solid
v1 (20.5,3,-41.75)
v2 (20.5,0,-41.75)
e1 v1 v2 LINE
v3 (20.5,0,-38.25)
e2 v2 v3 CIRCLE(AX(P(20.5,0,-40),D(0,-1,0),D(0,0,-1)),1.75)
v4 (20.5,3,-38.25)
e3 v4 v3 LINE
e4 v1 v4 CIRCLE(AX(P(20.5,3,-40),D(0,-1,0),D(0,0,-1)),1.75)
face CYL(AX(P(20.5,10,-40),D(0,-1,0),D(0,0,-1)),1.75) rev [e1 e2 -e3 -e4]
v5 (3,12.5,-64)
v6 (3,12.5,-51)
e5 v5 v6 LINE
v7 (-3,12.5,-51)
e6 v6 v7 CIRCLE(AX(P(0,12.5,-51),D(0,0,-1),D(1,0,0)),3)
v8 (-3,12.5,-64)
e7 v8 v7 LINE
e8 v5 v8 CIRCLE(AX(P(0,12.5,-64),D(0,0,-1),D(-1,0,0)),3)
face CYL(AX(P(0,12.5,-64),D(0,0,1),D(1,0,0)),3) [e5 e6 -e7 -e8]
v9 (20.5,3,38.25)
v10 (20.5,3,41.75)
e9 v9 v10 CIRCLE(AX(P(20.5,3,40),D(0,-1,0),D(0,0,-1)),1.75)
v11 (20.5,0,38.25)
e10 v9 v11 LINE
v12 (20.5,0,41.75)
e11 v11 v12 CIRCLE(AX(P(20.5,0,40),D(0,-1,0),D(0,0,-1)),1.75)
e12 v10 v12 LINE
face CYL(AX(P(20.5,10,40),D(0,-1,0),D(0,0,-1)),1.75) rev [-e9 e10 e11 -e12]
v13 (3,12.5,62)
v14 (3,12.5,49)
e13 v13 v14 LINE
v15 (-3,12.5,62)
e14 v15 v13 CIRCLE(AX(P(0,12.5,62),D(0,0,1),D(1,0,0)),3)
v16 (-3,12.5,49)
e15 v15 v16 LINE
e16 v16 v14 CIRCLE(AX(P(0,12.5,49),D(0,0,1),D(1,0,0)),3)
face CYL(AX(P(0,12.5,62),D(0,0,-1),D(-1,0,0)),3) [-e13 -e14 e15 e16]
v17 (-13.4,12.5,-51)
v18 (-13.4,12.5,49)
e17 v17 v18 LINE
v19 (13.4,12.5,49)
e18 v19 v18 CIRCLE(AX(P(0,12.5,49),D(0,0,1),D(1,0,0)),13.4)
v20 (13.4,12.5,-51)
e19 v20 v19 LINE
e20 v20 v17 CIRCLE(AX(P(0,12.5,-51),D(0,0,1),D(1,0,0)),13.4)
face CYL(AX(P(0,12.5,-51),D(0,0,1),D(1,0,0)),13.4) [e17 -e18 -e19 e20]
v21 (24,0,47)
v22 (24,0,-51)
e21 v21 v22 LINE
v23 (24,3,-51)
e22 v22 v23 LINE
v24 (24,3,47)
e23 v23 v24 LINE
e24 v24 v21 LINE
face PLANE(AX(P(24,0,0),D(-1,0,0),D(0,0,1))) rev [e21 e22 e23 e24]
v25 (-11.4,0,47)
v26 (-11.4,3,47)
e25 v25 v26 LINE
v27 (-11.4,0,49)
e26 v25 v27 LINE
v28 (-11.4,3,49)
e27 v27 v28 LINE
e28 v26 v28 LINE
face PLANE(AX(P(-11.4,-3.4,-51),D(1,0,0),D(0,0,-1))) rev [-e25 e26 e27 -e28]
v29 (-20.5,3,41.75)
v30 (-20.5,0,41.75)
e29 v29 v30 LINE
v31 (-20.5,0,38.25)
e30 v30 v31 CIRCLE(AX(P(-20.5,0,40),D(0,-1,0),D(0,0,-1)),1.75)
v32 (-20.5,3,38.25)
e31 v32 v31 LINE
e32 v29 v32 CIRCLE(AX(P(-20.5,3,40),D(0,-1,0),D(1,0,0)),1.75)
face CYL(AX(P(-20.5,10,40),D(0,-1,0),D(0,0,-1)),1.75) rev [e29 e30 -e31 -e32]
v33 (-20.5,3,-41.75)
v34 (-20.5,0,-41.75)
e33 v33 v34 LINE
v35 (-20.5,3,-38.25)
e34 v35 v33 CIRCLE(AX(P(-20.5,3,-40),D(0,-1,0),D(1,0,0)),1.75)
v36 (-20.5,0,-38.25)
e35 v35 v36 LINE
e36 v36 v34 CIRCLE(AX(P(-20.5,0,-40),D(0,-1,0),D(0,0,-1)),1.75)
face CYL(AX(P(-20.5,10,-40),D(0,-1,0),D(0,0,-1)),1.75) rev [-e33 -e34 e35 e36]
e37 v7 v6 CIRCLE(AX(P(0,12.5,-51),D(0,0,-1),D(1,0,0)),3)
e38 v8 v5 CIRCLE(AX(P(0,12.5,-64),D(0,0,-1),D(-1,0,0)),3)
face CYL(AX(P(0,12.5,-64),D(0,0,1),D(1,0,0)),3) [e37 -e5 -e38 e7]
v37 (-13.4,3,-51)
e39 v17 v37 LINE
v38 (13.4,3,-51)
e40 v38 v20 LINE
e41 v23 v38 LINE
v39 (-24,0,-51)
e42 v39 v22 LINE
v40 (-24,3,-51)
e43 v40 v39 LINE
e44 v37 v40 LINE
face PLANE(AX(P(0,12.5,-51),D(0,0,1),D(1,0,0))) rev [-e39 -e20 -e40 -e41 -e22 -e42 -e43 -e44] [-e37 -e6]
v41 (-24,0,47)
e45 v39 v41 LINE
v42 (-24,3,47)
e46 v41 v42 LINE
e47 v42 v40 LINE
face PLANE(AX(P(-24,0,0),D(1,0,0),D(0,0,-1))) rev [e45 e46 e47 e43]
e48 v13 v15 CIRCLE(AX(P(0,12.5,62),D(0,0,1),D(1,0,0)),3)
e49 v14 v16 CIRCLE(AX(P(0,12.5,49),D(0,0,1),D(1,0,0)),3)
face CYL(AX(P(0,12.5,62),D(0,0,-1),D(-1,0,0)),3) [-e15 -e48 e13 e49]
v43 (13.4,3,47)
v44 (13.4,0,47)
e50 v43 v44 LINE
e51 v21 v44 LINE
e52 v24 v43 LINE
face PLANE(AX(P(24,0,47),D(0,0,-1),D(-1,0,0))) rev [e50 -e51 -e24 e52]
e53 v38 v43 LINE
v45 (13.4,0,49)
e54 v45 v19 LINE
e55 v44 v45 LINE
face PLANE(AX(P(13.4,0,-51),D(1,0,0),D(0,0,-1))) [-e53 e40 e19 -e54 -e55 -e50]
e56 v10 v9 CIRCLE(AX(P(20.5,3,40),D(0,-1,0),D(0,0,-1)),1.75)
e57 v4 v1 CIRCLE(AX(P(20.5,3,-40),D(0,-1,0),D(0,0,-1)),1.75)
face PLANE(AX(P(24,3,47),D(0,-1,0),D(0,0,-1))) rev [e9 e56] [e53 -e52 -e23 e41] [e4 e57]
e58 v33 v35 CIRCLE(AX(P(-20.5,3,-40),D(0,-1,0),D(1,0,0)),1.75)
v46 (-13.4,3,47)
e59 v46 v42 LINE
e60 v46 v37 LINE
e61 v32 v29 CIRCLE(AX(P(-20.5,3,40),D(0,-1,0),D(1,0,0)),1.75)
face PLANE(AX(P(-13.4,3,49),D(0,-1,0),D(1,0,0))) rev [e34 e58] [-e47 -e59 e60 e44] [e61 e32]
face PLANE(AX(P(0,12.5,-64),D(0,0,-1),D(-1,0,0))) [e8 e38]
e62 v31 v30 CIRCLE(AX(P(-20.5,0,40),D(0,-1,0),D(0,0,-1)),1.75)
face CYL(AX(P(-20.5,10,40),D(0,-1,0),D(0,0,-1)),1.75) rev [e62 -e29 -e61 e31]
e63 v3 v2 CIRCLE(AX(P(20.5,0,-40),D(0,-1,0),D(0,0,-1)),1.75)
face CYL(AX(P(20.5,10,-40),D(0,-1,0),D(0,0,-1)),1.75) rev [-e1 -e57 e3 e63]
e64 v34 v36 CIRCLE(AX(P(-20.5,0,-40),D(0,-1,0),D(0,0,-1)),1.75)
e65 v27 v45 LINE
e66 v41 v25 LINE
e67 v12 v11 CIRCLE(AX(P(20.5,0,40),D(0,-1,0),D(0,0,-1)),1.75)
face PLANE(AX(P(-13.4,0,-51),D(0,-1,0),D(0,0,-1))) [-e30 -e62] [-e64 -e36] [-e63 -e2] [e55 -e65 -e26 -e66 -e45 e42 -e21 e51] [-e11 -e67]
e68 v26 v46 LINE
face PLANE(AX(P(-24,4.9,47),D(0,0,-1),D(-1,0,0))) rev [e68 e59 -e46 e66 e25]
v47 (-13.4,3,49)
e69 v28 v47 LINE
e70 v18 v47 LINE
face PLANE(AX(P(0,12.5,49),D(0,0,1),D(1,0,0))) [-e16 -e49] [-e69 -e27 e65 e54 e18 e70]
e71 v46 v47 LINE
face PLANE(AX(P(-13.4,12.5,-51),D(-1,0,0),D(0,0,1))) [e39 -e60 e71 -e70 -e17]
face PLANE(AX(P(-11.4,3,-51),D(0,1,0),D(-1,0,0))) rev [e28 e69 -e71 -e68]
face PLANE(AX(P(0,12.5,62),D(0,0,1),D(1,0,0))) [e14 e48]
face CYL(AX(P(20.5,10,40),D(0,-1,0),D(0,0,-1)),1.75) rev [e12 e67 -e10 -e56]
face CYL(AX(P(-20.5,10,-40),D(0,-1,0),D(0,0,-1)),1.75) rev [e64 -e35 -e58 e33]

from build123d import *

# Parameters (mm, degrees)
EXTRUDE_1_DEPTH     = 100
SKETCH_2_W          = 98
SKETCH_2_H          = 3
EXTRUDE_2_DEPTH     = 10.6
SKETCH_3_W          = 2
SKETCH_3_H          = 6.4
CUT_EXTRUDE_1_DEPTH = 107.050978308
SKETCH_4_W          = 98
SKETCH_4_H          = 4.9
EXTRUDE_3_DEPTH     = 12.6
SKETCH_5_W          = 10.6
SKETCH_5_H          = 1.9
CUT_EXTRUDE_2_DEPTH = 107.050978308
SKETCH_6_R          = 3
EXTRUDE_4_DEPTH     = 13
EXTRUDE_START       = 13
SKETCH_7_R          = 3
EXTRUDE_5_DEPTH     = 13
SKETCH_10_R         = 1.75
CUT_EXTRUDE_3_DEPTH = 10


with BuildPart() as part:
    # 草图1 → 凸台-拉伸1 (new body)
    with BuildSketch(Plane.XY.offset(49)):
        with BuildLine():
            Line((-13.4, 0), (13.4, 0))
            Line((13.4, 0), (13.4, 12.5))
            ThreePointArc((13.4, 12.5), (0, 25.9), (-13.4, 12.5))
            Line((-13.4, 12.5), (-13.4, 0))
        make_face()
    extrude(amount=-EXTRUDE_1_DEPTH)

    # 草图2 → 凸台-拉伸2 (add)
    with BuildSketch(Plane(origin=(13.4, 0, 0), x_dir=(0, 0, -1), z_dir=(1, 0, 0))):
        with Locations((2, 1.5)):
            Rectangle(SKETCH_2_W, SKETCH_2_H)
    extrude(amount=EXTRUDE_2_DEPTH)

    # 草图3 → 切除-拉伸1 (cut, through all)
    with BuildSketch(Plane.XY.offset(49)):
        with Locations((-12.4, -0.2)):
            Rectangle(SKETCH_3_W, SKETCH_3_H)
    extrude(amount=-CUT_EXTRUDE_1_DEPTH, mode=Mode.SUBTRACT)

    # 草图4 → 凸台-拉伸3 (add)
    with BuildSketch(Plane.ZY.offset(11.4)):
        with Locations((-2, 2.45)):
            Rectangle(SKETCH_4_W, SKETCH_4_H)
    extrude(amount=EXTRUDE_3_DEPTH)

    # 草图5 → 切除-拉伸2 (cut, through all)
    with BuildSketch(Plane(origin=(0, 0, -51), x_dir=(-1, 0, 0), z_dir=(0, 0, -1))):
        with Locations((18.7, 3.95)):
            Rectangle(SKETCH_5_W, SKETCH_5_H)
    extrude(amount=-CUT_EXTRUDE_2_DEPTH, mode=Mode.SUBTRACT)

    # 草图6 → 凸台-拉伸4 (add)
    with BuildSketch(Plane.XY.offset(49)):
        with Locations(Location((0, 12.5, 0), (0, 0, 180))):
            Circle(SKETCH_6_R)
    extrude(amount=EXTRUDE_4_DEPTH)

    # 草图7 → 凸台-拉伸5 (add)
    with BuildSketch(Plane(origin=(0, 0, -51), x_dir=(-1, 0, 0), z_dir=(0, 0, -1)).offset(EXTRUDE_START)):
        with Locations((0, 12.5)):
            Circle(SKETCH_7_R)
    extrude(amount=-EXTRUDE_5_DEPTH)

    # 草图10 → 切除-拉伸3 (cut)
    with BuildSketch(Plane.XZ):
        with Locations(Location((-20.5, 40, 0), (0, 0, 270))):
            Circle(SKETCH_10_R)
        with Locations(Location((20.5, 40, 0), (0, 0, 270))):
            Circle(SKETCH_10_R)
        with Locations(Location((20.5, -40, 0), (0, 0, 270))):
            Circle(SKETCH_10_R)
        with Locations(Location((-20.5, -40, 0), (0, 0, 270))):
            Circle(SKETCH_10_R)
    extrude(amount=-CUT_EXTRUDE_3_DEPTH, mode=Mode.SUBTRACT)


solid = part.part
